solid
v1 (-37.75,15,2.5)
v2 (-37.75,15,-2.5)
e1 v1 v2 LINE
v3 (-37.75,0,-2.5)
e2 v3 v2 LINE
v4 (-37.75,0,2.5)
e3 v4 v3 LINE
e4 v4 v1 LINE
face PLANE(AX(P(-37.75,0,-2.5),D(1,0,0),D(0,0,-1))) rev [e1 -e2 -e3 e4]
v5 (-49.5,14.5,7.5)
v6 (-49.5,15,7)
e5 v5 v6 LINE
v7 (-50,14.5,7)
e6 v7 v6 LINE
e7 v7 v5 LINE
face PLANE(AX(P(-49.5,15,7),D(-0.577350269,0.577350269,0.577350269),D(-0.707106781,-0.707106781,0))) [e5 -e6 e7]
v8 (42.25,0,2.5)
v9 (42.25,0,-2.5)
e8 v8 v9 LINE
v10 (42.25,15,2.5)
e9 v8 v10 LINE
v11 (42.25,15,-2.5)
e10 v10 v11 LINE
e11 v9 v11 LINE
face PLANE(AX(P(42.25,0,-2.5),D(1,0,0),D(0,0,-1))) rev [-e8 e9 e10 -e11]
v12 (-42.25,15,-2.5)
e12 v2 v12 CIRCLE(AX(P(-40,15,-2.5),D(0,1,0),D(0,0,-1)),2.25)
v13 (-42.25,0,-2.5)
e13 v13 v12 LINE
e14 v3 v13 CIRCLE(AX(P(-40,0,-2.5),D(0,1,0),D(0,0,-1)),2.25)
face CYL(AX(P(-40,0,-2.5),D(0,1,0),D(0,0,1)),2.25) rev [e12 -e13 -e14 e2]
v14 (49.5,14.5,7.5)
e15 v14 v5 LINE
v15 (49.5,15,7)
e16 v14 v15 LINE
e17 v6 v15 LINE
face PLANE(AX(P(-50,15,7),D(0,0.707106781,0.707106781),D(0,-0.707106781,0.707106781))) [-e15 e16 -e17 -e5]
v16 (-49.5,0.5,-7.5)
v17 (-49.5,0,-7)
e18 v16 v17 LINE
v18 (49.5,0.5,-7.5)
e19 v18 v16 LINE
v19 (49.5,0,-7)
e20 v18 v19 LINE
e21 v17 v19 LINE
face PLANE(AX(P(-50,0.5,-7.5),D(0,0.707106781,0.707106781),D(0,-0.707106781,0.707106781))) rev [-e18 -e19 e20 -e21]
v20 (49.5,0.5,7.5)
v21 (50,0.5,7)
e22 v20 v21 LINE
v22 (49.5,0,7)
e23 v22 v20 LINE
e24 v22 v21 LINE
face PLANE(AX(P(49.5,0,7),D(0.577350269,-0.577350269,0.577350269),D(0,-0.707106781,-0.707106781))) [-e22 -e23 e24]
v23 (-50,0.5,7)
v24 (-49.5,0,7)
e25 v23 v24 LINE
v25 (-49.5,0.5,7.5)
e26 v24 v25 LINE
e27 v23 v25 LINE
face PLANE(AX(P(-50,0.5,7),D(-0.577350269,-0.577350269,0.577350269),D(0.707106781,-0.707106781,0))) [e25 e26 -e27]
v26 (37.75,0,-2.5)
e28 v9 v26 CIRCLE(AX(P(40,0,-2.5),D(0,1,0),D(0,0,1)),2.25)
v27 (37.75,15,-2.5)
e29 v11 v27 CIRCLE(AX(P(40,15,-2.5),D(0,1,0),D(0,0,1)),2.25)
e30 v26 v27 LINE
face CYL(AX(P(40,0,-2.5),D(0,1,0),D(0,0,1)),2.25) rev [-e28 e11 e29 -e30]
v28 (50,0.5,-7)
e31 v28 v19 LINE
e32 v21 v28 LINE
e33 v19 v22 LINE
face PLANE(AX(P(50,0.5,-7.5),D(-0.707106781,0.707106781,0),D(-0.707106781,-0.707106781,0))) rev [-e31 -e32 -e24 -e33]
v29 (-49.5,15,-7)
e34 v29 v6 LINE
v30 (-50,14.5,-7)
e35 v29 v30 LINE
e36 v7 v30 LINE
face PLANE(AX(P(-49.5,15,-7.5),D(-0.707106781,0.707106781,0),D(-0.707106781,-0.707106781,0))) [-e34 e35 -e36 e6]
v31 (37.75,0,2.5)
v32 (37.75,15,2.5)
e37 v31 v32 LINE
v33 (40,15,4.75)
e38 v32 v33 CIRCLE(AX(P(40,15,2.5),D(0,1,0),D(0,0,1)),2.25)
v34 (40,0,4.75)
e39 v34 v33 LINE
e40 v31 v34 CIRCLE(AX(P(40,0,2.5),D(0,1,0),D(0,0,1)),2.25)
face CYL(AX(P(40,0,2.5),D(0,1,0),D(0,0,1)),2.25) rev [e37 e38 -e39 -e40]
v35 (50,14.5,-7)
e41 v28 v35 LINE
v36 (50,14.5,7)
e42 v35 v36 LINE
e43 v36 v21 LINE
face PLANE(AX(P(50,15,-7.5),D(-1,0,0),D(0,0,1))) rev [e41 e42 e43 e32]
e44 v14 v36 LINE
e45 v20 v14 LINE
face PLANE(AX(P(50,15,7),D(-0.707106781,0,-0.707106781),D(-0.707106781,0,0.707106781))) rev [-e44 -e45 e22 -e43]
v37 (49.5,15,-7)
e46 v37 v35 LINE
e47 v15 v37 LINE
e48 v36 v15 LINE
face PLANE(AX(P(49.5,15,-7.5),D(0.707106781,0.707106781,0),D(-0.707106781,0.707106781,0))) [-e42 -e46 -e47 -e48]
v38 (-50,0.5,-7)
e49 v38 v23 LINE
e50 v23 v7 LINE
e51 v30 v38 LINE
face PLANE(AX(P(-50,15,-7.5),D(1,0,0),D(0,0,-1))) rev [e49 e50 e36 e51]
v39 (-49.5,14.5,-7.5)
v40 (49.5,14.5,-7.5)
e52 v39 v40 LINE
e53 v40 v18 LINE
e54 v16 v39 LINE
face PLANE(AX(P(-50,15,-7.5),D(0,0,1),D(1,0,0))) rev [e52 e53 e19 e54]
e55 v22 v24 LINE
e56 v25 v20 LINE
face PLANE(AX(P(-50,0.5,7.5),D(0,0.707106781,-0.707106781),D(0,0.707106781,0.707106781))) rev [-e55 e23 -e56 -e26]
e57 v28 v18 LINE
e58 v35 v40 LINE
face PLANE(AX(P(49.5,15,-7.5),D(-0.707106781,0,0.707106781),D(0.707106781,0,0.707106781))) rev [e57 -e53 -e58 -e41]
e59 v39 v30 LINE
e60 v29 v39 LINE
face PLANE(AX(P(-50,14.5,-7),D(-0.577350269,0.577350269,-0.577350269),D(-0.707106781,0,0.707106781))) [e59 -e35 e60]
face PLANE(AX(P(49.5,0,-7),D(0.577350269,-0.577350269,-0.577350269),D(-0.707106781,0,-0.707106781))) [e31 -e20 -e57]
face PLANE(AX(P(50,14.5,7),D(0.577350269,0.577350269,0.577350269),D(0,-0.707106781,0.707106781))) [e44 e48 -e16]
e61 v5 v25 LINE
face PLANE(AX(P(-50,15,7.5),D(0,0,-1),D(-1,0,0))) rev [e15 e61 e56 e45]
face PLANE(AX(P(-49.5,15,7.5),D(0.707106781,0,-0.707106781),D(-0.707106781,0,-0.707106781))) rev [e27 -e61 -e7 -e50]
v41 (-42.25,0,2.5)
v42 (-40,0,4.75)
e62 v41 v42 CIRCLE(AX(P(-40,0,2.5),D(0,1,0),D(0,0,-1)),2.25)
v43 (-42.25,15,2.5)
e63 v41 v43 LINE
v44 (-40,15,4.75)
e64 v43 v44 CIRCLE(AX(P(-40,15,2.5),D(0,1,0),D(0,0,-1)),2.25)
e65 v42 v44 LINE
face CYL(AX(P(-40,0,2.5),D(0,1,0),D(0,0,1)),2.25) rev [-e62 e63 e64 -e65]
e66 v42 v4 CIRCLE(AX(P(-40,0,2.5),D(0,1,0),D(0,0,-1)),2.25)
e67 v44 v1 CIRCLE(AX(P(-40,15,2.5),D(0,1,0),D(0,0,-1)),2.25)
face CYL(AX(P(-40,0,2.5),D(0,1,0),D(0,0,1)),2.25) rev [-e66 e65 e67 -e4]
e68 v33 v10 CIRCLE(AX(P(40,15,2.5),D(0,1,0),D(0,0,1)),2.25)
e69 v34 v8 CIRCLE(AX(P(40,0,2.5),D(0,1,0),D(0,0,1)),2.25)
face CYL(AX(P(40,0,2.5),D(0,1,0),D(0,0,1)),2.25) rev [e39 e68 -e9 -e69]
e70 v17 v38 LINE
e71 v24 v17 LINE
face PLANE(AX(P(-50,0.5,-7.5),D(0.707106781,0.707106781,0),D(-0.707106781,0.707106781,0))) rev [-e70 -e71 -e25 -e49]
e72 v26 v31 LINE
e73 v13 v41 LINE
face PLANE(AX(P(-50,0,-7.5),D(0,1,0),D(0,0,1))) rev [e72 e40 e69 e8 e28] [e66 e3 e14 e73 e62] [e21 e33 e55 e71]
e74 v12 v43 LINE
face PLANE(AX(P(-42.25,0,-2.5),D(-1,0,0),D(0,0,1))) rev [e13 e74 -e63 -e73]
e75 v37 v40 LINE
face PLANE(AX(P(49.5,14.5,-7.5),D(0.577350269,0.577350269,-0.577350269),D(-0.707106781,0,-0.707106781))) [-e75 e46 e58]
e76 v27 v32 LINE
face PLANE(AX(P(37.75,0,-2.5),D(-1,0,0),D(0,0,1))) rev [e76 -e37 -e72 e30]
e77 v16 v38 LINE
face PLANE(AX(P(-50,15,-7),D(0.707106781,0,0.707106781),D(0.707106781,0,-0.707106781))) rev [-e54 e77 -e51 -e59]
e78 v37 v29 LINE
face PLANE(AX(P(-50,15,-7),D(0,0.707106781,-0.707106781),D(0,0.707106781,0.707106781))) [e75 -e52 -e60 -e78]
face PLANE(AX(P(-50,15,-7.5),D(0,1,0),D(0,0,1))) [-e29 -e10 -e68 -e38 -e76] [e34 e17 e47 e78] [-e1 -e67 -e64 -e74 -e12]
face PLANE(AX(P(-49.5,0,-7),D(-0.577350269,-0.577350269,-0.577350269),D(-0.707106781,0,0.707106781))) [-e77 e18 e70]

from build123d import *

# Parameters (mm, degrees)
SKETCH1_W          = 100
SKETCH1_H          = 15
EXTRUDE1_DEPTH     = 15
CUT_EXTRUDE1_DEPTH = 53.737557774
CHAMFER1_SIZE      = 0.5


with BuildPart() as part:
    # Sketch1 → Extrude1 (new body)
    with BuildSketch(Plane(origin=(0, 0, 0), x_dir=(1, 0, 0), z_dir=(0, 1, 0))):
        Rectangle(SKETCH1_W, SKETCH1_H)
    extrude(amount=EXTRUDE1_DEPTH)

    # Sketch4 → Cut-Extrude1 (cut, through all)
    with BuildSketch(Plane(origin=(0, 15, 0), x_dir=(1, 0, 0), z_dir=(0, 1, 0))):
        with BuildLine():
            Line((-42.25, 2.5), (-42.25, -2.5))
            ThreePointArc((-42.25, -2.5), (-40, -4.75), (-37.75, -2.5))
            Line((-37.75, -2.5), (-37.75, 2.5))
            ThreePointArc((-37.75, 2.5), (-40, 4.75), (-42.25, 2.5))
        make_face()
        with BuildLine():
            Line((37.75, 2.5), (37.75, -2.5))
            ThreePointArc((37.75, -2.5), (40, -4.75), (42.25, -2.5))
            Line((42.25, -2.5), (42.25, 2.5))
            ThreePointArc((42.25, 2.5), (40, 4.75), (37.75, 2.5))
        make_face()
    extrude(amount=-CUT_EXTRUDE1_DEPTH, mode=Mode.SUBTRACT)

    # Chamfer1
    chamfer1_edges = [part.edges().sort_by_distance(p)[0] for p in [
        (50, 15, 0),
        (0, 15, -7.5),
        (-50, 15, 0),
        (0, 0, -7.5),
        (50, 0, 0),
        (0, 0, 7.5),
        (-50, 0, 0),
        (0, 15, 7.5),
        (-50, 7.5, -7.5),
        (50, 7.5, -7.5),
        (50, 7.5, 7.5),
        (-50, 7.5, 7.5),
    ]]
    chamfer(chamfer1_edges, length=CHAMFER1_SIZE)


solid = part.part
